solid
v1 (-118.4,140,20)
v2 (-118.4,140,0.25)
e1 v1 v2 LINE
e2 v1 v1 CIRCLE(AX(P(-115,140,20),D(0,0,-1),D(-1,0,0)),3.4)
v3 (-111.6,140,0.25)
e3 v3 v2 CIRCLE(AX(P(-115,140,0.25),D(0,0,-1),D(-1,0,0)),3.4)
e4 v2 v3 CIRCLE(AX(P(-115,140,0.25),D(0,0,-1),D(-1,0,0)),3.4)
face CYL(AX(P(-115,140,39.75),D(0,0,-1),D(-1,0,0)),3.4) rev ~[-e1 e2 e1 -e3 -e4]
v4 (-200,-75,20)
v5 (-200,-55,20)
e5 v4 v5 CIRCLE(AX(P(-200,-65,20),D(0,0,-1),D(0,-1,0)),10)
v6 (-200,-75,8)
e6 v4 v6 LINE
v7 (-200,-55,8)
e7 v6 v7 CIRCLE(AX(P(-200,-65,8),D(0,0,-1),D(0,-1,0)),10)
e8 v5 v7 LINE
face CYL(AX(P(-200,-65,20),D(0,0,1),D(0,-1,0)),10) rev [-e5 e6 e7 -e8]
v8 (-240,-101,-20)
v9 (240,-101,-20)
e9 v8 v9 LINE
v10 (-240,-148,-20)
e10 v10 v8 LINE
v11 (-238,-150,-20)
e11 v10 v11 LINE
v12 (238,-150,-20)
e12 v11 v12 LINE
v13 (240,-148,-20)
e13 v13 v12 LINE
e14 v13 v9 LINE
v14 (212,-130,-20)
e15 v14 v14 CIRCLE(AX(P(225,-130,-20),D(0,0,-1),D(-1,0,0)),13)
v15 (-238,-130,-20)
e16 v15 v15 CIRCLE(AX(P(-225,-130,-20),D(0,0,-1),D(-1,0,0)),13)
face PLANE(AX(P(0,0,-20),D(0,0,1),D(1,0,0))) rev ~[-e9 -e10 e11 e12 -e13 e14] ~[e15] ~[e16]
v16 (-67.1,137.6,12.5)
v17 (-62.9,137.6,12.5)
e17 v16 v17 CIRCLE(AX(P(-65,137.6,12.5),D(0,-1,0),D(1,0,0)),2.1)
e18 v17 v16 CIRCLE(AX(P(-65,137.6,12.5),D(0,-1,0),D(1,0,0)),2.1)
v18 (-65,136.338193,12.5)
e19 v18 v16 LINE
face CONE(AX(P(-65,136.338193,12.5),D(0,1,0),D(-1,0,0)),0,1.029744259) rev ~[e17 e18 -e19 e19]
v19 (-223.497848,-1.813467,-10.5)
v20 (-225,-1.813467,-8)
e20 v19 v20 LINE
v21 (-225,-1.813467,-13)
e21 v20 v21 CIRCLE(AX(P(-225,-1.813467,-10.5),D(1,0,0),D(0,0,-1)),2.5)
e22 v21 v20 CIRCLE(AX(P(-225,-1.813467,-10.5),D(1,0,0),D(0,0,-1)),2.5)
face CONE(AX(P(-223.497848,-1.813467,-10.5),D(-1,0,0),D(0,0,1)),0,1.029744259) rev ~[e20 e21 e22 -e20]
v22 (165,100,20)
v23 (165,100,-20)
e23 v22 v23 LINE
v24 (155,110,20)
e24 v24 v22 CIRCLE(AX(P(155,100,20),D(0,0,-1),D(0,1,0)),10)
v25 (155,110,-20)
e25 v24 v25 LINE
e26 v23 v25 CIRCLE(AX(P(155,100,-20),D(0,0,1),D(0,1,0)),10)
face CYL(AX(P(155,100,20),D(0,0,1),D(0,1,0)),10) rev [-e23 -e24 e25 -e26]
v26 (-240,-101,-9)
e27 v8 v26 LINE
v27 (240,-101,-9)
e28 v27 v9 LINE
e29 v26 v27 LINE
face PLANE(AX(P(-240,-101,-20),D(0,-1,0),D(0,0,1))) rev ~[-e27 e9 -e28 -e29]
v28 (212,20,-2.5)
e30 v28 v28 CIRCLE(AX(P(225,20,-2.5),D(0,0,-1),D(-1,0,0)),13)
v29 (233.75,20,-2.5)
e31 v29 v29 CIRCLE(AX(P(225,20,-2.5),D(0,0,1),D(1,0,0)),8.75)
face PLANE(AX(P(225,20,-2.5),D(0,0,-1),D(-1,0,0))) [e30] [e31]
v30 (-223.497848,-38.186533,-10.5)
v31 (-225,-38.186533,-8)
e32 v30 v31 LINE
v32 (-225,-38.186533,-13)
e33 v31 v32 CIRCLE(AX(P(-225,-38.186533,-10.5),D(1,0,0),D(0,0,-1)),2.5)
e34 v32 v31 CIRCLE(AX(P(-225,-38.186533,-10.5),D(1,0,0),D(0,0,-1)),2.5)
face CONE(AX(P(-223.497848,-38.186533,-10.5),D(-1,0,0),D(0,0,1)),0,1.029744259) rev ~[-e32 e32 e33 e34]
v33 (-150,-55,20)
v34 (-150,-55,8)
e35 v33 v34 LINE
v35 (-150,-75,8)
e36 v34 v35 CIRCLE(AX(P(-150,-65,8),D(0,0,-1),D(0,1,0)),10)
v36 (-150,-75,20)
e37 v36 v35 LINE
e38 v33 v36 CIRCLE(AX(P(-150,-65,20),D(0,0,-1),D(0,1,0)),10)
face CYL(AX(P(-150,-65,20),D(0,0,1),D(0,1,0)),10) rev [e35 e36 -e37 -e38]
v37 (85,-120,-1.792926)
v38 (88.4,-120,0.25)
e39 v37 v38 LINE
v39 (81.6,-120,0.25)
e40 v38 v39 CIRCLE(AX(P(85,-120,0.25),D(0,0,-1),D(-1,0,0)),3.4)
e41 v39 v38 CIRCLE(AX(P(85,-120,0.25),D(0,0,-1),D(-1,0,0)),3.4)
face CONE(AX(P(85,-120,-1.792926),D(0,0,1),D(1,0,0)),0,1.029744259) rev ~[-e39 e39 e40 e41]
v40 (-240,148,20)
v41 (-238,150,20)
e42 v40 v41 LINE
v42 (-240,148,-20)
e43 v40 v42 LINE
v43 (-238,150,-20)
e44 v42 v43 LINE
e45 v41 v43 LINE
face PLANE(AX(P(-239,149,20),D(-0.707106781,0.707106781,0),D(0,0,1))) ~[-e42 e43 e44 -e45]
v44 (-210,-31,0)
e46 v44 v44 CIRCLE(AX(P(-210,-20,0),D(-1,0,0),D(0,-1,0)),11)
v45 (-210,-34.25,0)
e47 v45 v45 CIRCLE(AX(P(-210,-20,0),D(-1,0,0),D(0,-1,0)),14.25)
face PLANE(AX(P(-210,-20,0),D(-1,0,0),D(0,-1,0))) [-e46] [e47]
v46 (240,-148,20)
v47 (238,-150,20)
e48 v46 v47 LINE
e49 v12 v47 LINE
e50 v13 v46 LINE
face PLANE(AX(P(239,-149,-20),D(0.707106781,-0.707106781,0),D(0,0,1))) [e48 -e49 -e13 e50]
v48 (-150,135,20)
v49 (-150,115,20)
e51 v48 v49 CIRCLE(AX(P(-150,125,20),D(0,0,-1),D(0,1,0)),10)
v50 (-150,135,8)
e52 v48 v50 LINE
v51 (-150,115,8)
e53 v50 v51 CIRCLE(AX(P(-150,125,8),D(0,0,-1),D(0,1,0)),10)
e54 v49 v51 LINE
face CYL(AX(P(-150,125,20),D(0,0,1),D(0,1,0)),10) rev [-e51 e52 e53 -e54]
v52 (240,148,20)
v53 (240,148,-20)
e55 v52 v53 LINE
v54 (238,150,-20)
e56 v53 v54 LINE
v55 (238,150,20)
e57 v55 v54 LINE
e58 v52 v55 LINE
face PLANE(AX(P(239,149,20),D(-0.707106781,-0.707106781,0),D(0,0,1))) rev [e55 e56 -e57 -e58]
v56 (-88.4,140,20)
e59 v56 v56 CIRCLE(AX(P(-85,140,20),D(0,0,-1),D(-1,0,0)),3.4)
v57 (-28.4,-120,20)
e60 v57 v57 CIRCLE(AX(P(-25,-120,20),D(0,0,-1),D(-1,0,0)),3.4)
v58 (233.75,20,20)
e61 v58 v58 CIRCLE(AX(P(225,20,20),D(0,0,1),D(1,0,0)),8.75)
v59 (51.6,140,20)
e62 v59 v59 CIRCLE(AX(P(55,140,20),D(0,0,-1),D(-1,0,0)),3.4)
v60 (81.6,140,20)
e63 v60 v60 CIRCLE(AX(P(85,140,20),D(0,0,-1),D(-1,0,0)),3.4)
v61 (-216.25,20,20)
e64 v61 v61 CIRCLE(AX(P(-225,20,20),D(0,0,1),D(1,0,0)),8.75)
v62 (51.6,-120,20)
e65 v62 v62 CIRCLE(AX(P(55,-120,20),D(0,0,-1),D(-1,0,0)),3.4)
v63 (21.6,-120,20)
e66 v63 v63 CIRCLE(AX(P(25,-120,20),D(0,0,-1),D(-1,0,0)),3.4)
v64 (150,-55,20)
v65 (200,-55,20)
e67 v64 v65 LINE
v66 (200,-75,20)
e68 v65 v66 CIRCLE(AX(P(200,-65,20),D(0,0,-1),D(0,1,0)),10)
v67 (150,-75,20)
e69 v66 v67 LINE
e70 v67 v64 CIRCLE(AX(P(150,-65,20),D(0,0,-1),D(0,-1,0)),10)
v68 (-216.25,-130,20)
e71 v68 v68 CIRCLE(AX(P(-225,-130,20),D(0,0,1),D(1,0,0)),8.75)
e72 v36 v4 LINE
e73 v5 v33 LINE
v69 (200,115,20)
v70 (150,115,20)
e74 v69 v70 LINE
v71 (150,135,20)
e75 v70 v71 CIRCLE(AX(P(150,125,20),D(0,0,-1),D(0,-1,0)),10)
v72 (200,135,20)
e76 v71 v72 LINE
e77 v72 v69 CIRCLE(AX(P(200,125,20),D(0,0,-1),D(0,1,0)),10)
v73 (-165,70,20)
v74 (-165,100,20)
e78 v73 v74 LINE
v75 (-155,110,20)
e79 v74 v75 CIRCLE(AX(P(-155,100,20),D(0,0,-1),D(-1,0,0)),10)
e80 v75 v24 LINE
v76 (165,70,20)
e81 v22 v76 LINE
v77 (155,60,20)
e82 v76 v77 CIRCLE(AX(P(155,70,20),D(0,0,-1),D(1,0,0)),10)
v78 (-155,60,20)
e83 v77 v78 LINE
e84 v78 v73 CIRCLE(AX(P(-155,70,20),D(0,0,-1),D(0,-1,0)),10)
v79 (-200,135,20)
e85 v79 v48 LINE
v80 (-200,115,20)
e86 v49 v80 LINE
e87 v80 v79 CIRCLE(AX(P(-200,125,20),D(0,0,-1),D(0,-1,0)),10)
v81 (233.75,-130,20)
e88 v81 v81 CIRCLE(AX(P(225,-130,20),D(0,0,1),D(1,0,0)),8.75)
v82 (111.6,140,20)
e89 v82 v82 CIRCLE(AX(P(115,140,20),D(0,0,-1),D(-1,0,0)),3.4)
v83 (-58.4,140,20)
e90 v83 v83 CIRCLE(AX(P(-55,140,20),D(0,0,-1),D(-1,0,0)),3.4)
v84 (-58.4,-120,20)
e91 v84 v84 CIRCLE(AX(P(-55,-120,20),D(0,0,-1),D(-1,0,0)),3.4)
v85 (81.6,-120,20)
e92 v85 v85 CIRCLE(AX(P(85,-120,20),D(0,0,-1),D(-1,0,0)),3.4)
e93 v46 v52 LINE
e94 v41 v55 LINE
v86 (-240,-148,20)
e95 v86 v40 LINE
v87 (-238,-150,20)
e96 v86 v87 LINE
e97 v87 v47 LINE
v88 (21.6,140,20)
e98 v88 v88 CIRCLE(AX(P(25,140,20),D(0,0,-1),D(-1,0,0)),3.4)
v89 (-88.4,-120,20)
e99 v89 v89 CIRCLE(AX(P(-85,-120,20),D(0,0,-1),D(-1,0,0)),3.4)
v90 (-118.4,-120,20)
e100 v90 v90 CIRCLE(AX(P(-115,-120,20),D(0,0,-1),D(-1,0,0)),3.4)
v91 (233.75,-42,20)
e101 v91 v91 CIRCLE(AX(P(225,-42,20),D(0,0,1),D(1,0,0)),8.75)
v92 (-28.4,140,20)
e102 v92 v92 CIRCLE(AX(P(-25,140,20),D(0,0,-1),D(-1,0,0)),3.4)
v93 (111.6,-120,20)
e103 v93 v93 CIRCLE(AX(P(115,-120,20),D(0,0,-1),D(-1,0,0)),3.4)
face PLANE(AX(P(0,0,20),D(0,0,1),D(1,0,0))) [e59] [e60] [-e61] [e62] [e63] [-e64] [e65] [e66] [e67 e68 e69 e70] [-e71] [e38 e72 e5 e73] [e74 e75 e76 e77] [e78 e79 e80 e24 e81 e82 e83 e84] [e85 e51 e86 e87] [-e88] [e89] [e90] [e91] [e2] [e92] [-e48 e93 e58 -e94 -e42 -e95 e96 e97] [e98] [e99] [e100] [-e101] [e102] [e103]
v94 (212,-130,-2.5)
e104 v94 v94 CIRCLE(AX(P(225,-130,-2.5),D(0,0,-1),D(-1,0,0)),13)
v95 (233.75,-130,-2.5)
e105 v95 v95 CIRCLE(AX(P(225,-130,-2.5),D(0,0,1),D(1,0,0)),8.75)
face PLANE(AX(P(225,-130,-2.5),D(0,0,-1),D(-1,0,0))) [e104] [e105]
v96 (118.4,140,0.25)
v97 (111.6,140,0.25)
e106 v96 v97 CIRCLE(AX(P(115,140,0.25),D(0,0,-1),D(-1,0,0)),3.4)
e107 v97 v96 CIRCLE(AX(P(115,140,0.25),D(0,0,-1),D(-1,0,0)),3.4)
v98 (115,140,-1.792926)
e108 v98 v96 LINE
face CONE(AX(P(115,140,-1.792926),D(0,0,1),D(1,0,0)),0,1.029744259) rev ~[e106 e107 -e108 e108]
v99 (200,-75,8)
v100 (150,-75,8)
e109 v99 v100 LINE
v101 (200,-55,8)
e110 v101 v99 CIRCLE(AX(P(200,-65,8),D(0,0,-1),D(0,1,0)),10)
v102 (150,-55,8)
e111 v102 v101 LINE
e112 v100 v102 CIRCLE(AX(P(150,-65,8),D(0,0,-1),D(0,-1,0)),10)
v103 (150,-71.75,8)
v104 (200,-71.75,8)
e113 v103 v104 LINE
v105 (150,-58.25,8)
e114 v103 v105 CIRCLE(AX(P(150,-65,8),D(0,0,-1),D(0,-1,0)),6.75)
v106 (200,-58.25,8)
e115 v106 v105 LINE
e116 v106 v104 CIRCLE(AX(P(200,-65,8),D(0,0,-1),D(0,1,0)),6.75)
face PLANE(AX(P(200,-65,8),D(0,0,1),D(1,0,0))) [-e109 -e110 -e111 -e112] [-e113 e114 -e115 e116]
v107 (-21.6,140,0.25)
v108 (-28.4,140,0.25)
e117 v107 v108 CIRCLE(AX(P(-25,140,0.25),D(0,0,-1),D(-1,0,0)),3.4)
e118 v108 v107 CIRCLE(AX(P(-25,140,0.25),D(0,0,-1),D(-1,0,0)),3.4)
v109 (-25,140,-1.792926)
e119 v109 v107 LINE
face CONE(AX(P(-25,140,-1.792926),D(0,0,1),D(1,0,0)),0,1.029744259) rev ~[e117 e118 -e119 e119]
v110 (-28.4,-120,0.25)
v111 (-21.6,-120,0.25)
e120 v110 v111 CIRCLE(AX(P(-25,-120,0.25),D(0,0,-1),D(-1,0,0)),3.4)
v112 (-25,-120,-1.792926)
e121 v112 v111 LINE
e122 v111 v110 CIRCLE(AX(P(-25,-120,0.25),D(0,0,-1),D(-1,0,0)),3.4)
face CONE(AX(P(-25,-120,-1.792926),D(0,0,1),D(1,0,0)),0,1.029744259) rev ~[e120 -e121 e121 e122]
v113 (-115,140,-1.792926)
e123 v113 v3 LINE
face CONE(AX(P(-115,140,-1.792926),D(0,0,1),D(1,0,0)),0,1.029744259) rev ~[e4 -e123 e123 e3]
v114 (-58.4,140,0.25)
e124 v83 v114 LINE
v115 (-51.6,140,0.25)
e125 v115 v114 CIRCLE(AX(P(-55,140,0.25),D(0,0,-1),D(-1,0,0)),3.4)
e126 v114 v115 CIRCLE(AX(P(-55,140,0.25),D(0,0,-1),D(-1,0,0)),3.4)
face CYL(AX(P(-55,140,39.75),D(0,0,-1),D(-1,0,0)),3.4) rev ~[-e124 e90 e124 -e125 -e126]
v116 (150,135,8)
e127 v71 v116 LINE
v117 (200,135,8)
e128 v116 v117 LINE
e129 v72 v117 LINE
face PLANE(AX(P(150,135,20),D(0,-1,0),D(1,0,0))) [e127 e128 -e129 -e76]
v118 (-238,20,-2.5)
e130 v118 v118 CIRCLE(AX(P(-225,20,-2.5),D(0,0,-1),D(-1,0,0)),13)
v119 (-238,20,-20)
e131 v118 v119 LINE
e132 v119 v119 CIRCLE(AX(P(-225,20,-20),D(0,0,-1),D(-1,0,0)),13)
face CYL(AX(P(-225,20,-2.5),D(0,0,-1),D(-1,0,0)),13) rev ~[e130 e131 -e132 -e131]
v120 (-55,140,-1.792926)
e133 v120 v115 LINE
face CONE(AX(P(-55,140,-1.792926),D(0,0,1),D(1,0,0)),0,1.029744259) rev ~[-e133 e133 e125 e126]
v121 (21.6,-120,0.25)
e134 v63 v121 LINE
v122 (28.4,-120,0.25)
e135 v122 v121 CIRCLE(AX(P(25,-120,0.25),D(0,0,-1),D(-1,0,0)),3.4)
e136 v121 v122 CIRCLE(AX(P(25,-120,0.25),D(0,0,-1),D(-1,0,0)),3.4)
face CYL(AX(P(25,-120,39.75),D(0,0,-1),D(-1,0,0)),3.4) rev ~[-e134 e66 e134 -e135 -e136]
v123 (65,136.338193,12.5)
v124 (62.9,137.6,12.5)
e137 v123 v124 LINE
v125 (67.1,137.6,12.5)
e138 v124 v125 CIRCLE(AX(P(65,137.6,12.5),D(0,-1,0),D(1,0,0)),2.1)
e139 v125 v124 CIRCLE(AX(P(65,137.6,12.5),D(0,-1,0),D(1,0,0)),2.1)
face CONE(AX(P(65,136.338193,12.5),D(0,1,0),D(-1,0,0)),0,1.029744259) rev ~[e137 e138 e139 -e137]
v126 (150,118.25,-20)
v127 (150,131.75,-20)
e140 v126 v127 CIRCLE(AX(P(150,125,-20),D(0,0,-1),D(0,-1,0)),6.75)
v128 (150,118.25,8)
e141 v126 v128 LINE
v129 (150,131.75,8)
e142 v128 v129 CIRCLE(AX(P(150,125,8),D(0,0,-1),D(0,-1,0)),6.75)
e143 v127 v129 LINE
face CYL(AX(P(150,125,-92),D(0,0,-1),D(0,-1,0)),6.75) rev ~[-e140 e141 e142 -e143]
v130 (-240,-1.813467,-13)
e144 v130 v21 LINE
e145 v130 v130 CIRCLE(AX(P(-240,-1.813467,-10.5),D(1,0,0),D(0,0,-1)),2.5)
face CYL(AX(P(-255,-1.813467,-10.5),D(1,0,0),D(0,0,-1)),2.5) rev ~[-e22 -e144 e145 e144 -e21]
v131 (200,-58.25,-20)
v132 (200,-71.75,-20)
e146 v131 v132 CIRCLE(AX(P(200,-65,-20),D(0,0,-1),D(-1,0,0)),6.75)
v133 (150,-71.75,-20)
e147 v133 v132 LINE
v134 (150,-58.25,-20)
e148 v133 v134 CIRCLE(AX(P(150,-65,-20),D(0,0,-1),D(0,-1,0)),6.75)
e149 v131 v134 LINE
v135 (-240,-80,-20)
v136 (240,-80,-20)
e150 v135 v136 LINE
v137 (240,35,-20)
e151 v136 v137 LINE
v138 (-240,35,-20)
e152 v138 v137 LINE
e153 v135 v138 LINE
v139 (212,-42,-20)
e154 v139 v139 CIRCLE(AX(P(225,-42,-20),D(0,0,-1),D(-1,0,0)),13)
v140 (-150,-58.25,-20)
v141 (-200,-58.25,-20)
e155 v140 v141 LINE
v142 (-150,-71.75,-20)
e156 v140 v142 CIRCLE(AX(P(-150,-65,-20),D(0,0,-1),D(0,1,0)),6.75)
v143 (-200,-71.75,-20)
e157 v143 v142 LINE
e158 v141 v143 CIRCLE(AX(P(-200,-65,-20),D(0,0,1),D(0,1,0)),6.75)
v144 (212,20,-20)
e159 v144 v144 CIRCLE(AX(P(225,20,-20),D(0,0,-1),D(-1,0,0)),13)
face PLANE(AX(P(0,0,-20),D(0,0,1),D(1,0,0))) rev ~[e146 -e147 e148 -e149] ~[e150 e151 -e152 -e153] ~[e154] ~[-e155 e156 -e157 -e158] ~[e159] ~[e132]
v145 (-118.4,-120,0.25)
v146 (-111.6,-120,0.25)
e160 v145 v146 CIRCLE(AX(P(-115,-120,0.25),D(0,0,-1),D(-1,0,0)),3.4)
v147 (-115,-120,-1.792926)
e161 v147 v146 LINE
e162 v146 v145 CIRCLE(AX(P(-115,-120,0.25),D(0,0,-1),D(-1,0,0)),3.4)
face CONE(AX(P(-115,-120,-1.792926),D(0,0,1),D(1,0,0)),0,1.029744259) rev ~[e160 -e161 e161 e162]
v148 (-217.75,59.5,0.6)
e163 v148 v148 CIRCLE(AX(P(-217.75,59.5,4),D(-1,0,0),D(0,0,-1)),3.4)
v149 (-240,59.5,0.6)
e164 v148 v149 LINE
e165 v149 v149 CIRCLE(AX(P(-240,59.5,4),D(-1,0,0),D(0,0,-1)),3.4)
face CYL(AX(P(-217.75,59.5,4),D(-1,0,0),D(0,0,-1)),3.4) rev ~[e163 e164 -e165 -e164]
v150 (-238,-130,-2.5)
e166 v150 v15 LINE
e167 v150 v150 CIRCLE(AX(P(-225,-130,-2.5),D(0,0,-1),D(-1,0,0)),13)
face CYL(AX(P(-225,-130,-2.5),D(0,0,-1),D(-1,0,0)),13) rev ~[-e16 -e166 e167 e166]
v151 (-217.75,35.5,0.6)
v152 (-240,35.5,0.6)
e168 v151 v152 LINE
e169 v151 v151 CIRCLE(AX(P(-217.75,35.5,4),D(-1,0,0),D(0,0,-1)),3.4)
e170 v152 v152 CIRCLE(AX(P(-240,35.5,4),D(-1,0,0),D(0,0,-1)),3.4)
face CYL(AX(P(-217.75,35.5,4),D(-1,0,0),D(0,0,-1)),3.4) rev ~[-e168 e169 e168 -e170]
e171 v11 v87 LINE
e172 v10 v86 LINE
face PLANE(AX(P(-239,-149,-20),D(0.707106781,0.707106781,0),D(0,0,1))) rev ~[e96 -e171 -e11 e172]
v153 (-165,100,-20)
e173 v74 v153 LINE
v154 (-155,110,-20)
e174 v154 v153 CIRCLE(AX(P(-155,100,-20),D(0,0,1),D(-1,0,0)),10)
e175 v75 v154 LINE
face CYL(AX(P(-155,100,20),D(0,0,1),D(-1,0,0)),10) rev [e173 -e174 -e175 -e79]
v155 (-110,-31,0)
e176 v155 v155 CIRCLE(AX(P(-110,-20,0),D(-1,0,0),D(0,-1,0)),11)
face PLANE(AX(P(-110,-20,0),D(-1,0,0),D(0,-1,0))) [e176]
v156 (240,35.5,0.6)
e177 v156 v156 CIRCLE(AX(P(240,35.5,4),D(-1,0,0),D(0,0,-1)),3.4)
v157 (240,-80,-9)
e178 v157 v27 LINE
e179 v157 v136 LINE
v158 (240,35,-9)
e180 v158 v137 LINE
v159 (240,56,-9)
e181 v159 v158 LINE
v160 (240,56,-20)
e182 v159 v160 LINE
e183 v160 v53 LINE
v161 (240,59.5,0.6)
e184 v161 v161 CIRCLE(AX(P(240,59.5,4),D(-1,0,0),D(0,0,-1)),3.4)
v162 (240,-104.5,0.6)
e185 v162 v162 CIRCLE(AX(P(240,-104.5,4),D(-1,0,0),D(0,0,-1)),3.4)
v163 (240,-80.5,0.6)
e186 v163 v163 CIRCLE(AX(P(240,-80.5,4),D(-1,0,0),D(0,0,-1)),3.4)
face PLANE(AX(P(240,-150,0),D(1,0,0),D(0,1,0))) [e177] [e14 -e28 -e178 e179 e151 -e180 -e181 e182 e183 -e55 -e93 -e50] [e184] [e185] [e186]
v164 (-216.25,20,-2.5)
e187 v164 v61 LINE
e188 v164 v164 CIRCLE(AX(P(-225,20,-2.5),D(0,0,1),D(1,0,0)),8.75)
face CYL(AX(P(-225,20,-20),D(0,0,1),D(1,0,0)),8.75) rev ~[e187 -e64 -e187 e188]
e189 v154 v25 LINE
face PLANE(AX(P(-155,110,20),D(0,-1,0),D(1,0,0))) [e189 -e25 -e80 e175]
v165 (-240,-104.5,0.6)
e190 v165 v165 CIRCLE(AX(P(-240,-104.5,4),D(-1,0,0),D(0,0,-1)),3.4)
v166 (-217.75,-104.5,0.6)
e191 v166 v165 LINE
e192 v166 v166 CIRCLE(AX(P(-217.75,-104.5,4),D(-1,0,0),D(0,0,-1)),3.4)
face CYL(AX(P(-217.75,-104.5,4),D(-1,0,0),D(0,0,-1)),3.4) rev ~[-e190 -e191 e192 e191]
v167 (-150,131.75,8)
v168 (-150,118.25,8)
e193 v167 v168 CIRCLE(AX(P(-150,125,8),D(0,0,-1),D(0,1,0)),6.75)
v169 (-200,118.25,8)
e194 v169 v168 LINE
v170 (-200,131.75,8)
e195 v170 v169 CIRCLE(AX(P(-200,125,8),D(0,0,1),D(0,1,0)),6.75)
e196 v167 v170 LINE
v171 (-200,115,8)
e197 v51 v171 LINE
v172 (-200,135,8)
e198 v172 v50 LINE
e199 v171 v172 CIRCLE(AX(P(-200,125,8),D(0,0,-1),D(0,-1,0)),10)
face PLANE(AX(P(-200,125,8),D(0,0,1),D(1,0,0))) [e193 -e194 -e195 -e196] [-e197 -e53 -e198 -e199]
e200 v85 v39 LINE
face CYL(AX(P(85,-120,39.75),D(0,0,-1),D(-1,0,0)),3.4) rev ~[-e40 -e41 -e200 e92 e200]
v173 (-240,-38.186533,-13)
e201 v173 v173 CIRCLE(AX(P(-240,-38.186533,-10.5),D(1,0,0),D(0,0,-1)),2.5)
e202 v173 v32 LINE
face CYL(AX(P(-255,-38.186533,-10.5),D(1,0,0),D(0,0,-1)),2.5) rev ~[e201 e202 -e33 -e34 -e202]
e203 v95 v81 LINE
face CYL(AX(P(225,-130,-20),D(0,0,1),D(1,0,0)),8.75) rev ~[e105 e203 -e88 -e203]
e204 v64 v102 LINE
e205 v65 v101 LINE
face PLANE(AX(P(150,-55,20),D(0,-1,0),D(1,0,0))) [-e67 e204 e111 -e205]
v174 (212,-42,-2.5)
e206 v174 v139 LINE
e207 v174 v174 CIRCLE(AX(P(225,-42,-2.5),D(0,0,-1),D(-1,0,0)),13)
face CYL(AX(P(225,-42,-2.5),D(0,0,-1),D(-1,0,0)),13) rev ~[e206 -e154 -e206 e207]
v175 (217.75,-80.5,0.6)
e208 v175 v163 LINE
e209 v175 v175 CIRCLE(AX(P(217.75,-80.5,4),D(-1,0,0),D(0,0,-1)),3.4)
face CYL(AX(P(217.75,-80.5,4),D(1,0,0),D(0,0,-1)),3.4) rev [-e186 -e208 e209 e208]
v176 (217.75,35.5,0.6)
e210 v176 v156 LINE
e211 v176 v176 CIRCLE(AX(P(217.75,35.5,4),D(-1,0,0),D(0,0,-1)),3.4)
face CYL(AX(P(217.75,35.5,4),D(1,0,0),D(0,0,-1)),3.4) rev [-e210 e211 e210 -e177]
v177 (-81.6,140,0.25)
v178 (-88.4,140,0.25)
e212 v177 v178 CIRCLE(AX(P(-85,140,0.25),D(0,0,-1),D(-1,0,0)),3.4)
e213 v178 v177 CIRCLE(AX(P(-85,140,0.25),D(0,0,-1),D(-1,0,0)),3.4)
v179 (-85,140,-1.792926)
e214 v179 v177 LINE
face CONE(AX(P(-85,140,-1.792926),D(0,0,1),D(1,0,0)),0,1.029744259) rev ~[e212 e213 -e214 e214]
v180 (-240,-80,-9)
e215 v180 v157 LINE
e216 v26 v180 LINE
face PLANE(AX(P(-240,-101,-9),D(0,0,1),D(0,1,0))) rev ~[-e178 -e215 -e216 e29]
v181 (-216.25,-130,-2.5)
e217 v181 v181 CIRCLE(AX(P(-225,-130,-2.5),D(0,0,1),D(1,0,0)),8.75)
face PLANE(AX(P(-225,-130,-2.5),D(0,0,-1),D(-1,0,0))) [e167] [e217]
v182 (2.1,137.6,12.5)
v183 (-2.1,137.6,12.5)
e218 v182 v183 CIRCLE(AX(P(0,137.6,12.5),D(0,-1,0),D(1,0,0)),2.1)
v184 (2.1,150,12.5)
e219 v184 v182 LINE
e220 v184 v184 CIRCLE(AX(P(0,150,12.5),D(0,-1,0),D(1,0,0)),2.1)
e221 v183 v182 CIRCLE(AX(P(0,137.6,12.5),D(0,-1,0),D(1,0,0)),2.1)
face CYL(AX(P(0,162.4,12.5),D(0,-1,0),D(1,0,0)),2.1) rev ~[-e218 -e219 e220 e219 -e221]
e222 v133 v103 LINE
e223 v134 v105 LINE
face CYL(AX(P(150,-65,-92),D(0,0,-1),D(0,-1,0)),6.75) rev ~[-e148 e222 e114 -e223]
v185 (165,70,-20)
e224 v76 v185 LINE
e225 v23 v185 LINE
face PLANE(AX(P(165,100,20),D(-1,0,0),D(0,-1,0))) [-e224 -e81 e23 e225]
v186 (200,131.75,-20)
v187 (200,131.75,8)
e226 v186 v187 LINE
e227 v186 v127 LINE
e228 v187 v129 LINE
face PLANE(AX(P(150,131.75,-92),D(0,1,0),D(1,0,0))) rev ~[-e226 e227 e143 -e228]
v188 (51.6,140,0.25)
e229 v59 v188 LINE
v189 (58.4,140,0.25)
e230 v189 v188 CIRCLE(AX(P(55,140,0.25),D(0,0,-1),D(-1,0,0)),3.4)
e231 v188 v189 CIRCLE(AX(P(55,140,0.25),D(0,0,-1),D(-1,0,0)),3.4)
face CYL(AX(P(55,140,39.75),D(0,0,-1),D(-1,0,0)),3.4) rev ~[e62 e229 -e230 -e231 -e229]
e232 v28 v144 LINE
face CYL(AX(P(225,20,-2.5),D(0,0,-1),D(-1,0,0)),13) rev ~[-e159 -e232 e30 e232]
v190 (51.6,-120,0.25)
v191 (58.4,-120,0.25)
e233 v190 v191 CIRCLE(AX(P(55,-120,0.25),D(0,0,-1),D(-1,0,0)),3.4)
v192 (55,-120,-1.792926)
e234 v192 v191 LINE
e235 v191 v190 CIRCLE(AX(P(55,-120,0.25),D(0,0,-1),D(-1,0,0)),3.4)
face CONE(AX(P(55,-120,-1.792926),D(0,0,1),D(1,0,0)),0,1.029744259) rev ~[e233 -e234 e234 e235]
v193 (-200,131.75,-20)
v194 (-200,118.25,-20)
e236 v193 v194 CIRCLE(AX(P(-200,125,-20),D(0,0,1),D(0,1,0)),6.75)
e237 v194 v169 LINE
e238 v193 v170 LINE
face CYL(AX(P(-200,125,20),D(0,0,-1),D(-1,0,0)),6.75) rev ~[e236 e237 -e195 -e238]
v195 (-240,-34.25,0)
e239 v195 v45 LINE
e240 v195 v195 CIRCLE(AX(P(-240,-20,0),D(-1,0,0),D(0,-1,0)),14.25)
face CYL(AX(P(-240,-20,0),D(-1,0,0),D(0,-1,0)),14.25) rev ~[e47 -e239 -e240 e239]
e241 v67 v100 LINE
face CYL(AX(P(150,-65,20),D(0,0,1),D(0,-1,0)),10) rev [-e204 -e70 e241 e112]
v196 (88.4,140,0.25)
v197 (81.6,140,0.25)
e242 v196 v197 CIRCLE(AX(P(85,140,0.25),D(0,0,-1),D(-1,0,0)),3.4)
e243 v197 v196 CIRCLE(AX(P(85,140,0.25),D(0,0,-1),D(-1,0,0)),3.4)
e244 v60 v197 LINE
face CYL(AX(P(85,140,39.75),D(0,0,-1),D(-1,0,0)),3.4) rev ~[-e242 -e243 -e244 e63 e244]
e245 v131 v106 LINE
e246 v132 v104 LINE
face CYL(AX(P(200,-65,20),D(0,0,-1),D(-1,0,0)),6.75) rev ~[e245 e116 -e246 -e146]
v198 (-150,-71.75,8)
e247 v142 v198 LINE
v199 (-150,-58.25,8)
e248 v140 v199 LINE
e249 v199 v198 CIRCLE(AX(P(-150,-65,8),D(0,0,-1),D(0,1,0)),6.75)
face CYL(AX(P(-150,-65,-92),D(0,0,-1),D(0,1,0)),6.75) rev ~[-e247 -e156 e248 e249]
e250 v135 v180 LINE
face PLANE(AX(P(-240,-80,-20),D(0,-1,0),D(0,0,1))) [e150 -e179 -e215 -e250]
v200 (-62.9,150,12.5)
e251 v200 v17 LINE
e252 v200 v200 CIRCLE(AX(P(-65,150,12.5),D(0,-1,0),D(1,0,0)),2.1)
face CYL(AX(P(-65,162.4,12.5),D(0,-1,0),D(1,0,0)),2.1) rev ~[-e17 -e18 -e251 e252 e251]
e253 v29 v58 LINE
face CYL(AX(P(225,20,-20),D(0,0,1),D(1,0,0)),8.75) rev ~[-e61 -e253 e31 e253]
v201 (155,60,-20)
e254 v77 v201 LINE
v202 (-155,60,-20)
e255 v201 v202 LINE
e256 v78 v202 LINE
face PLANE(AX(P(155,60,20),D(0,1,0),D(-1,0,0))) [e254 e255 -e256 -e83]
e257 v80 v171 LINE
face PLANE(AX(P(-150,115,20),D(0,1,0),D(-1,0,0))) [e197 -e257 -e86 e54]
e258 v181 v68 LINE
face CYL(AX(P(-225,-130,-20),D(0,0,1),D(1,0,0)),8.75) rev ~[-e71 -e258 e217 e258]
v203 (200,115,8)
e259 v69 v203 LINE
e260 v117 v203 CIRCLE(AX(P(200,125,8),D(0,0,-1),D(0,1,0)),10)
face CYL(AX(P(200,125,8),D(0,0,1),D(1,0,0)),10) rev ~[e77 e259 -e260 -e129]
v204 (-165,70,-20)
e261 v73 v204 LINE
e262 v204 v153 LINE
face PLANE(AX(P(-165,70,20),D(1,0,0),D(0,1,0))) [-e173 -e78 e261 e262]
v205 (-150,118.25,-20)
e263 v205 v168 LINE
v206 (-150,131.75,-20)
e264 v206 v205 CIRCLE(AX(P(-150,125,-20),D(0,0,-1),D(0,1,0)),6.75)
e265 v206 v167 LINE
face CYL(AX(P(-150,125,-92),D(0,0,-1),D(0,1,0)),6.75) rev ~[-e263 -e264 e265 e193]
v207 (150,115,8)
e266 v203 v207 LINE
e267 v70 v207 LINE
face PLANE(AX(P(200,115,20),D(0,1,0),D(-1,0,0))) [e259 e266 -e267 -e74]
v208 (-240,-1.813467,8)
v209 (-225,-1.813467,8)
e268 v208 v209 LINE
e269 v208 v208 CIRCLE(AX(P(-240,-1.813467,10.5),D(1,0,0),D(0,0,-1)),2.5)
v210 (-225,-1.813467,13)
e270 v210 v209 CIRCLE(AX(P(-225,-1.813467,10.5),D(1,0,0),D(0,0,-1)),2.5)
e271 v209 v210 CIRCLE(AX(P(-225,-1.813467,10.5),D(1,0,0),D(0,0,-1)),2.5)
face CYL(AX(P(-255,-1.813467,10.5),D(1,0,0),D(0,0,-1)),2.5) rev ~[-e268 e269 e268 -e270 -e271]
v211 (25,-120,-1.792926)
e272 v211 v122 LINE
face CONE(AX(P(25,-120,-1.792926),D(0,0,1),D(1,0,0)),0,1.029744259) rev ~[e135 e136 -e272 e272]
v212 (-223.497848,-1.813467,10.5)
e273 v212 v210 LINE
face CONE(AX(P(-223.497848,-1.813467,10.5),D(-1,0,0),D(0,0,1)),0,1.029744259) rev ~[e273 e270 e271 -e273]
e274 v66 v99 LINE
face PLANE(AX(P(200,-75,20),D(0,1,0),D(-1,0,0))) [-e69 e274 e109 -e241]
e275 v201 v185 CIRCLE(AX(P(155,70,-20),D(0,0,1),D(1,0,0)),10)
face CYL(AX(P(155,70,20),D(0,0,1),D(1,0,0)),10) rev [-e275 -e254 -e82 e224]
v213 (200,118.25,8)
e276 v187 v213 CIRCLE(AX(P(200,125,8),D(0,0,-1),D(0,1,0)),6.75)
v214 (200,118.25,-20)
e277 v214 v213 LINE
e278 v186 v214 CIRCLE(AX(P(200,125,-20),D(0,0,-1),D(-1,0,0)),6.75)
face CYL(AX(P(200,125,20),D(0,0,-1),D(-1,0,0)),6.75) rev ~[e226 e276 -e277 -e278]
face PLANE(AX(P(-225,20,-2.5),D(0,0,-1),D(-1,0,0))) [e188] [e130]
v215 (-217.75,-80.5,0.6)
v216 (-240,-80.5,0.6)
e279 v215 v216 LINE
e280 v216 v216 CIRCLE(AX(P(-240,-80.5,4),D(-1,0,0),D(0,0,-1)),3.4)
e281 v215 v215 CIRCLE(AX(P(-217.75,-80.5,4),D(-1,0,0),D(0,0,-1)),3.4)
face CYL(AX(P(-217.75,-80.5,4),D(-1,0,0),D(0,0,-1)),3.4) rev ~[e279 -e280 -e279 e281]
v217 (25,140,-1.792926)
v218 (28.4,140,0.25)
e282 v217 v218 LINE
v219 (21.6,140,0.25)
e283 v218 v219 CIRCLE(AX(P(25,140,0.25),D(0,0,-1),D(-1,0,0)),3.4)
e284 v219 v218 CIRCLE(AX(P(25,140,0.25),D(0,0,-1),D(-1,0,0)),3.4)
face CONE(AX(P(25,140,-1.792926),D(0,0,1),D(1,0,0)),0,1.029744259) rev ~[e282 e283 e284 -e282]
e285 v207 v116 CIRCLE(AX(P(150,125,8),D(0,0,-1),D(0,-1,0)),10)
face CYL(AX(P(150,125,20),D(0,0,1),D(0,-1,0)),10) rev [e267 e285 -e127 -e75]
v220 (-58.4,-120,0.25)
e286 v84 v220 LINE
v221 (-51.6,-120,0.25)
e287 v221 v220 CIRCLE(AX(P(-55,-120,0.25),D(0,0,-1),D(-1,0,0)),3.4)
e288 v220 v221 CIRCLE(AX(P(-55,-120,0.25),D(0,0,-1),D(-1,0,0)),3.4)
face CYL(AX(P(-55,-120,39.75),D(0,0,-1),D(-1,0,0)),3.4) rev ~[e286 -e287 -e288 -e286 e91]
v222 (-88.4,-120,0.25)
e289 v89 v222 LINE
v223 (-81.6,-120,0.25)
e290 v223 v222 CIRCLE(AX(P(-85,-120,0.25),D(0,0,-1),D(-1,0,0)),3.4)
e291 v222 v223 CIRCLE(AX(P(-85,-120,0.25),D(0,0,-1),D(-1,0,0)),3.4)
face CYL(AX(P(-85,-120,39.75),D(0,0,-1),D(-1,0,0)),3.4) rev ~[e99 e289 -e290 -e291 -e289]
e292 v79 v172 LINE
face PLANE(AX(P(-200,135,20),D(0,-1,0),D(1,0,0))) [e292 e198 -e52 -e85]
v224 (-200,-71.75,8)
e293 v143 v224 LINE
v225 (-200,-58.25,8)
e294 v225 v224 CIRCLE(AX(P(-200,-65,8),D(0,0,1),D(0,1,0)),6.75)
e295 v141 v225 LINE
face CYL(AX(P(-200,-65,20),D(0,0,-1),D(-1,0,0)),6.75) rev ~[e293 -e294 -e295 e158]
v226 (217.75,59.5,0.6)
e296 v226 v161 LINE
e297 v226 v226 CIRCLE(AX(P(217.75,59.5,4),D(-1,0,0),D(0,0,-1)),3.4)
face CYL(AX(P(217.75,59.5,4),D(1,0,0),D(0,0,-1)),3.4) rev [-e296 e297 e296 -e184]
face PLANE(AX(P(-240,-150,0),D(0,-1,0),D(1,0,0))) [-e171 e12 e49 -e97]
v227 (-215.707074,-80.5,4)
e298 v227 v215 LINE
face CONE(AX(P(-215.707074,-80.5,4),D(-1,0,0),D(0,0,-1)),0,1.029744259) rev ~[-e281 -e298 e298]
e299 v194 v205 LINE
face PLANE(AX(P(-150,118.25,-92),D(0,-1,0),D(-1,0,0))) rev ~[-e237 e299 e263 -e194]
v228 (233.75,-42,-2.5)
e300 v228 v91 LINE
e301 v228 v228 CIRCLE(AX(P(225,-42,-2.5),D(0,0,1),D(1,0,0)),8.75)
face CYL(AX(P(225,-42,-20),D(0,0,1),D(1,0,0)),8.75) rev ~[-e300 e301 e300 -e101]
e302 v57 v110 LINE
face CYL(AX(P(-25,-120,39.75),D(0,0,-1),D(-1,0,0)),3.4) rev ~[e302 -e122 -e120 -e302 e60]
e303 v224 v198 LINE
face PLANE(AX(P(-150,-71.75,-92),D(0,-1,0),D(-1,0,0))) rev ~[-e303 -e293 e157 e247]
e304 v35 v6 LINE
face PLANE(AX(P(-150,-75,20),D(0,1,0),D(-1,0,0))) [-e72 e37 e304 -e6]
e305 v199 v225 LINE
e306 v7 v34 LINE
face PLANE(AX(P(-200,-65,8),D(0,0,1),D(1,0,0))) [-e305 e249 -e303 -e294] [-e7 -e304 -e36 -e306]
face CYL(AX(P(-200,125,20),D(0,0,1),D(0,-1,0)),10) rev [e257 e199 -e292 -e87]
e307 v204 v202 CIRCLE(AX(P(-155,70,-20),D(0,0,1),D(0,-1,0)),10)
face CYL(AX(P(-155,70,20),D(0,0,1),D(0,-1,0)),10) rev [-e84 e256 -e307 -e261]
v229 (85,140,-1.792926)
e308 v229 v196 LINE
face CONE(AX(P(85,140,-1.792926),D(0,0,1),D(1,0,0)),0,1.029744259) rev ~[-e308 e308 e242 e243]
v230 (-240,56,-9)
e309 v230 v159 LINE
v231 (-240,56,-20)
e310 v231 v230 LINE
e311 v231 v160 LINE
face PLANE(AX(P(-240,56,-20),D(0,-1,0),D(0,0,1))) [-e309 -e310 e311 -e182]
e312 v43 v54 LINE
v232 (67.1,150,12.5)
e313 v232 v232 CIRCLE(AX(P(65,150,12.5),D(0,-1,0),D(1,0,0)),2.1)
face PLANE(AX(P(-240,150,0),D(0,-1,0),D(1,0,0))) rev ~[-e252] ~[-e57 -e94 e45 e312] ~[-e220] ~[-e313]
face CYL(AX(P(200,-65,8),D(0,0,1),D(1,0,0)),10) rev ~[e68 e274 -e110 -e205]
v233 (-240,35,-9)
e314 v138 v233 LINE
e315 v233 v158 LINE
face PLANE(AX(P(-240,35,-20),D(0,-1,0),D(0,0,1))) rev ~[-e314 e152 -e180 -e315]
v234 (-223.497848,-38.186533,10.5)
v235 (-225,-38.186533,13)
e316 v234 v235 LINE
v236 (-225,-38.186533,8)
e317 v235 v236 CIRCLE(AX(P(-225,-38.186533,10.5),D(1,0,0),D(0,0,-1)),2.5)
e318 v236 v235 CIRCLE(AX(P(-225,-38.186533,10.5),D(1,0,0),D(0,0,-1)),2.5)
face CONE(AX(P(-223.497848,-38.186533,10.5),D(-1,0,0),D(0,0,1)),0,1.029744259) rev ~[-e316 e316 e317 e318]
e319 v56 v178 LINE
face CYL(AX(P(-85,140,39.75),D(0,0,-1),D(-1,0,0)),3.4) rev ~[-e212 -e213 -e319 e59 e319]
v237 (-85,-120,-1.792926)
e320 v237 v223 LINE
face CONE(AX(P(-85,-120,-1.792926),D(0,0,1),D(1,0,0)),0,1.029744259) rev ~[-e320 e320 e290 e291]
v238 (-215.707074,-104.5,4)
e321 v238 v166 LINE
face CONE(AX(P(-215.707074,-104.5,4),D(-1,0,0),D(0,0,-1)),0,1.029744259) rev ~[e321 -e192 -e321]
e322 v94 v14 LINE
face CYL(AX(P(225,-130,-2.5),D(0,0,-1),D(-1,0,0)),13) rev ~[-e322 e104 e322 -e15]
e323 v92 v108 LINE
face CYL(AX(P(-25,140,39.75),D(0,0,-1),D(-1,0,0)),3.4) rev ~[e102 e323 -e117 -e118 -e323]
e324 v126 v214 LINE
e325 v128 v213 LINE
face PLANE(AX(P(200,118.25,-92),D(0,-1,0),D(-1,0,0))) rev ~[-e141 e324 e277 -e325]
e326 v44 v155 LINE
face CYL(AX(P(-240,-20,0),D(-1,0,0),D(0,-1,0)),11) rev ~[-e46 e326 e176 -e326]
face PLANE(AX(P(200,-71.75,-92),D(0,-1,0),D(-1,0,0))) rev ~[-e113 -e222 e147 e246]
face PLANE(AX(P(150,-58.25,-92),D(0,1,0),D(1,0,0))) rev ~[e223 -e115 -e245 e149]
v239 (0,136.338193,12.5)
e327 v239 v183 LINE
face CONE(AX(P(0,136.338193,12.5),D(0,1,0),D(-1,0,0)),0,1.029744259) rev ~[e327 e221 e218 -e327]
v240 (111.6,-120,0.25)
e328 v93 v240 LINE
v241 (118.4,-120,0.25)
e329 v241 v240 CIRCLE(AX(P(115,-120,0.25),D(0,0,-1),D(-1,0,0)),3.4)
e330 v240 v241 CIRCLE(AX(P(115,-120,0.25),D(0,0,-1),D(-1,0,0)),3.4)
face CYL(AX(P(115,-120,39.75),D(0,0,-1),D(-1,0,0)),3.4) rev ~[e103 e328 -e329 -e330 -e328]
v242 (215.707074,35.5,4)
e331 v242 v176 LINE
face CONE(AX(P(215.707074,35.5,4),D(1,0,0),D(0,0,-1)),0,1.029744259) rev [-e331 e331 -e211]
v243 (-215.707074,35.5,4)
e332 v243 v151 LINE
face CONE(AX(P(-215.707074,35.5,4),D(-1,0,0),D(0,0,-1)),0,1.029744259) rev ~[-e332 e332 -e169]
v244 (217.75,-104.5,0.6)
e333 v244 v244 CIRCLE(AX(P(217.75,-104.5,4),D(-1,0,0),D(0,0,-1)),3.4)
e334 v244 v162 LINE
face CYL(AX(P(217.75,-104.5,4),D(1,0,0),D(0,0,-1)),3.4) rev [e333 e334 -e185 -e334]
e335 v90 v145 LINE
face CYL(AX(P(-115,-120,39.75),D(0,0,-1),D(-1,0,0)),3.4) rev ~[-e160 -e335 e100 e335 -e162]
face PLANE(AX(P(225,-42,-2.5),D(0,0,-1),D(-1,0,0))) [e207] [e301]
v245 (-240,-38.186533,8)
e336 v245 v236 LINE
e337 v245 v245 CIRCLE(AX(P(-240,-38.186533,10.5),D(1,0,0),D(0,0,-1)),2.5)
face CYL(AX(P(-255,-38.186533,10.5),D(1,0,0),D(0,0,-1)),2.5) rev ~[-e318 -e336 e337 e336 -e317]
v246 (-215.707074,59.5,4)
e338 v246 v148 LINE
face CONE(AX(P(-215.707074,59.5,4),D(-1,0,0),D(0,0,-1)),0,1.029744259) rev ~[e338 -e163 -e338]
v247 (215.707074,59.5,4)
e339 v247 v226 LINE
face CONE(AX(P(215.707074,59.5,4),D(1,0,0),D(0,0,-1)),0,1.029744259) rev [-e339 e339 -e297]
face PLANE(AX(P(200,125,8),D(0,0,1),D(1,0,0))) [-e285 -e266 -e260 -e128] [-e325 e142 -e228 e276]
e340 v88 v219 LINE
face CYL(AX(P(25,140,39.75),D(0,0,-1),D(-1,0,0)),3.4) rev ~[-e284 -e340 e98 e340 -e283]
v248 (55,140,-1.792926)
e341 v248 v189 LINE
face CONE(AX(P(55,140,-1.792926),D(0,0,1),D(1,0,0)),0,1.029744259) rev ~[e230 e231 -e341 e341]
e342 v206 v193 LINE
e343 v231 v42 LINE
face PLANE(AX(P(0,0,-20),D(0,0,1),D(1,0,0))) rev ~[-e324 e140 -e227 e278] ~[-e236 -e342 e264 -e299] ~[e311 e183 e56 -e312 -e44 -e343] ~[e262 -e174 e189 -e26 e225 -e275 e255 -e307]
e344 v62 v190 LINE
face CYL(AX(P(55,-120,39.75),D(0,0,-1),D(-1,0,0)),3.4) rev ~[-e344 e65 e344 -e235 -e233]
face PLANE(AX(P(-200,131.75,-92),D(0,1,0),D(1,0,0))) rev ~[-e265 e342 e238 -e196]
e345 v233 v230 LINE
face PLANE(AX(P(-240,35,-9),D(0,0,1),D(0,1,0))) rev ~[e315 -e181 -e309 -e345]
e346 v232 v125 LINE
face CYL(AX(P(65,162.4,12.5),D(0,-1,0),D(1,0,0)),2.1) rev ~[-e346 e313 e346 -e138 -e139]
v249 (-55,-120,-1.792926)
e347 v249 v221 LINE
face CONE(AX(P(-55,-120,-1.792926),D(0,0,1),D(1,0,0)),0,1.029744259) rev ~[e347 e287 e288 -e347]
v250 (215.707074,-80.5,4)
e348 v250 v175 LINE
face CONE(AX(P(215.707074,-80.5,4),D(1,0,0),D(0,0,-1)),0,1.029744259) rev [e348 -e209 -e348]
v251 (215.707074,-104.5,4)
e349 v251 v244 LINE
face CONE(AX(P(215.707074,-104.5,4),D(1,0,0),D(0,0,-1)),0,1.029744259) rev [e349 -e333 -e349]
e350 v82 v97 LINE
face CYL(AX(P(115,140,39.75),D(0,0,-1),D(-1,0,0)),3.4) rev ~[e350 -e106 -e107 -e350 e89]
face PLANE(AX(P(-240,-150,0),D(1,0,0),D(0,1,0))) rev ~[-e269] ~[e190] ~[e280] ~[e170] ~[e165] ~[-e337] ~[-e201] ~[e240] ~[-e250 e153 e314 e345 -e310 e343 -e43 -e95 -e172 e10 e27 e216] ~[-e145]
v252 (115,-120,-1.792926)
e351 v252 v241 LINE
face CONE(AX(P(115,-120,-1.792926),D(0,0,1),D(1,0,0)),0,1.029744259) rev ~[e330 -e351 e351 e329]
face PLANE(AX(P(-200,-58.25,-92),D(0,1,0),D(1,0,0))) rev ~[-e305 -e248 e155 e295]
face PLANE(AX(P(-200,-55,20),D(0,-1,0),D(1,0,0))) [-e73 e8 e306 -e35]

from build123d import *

# Parameters (mm, degrees)
SKETCH1_W                                            = 480
SKETCH1_H                                            = 300
BOSS_EXTRUDE1_DEPTH                                  = 20
CUT_EXTRUDE1_DEPTH                                   = 286.832118559
HOLE_SIZE_PER_SOCKET_HEAD_CAP_SCREW_TYPE_D           = 17.5
HOLE_SIZE_PER_SOCKET_HEAD_CAP_SCREW_TYPE_CBORE_D     = 26
HOLE_SIZE_PER_SOCKET_HEAD_CAP_SCREW_TYPE_CBORE_DEPTH = 17.5
CBORE_FOR_M12_HEX_SOCKET_HEAD_CAP_SCREW1_D           = 13.5
CBORE_FOR_M12_HEX_SOCKET_HEAD_CAP_SCREW1_CBORE_D     = 20
CBORE_FOR_M12_HEX_SOCKET_HEAD_CAP_SCREW1_CBORE_DEPTH = 12
SKETCH7_W                                            = 11
SKETCH7_H                                            = 21
CUT_EXTRUDE2_DEPTH                                   = 504.289181286
M5_TAPPED_HOLE1_D                                    = 4.2
M5_TAPPED_HOLE1_DEPTH                                = 12.4
M5_TAPPED_HOLE1_TIP                                  = 1.2618073
CUT_EXTRUDE5_START                                   = -100
CUT_EXTRUDE5_DEPTH                                   = 100
CUT_EXTRUDE6_DEPTH                                   = 12
CHAMFER1_SIZE                                        = 2
M8_TAPPED_HOLE1_D                                    = 6.8
M8_TAPPED_HOLE1_DEPTH                                = 19.75
M8_TAPPED_HOLE1_TIP                                  = 2.042926105
SKETCH29_R                                           = 11
CUT_EXTRUDE7_DEPTH                                   = 130
SKETCH30_R                                           = 14.25
CUT_EXTRUDE8_DEPTH                                   = 30
M6_TAPPED_HOLE2_D                                    = 5
M6_TAPPED_HOLE2_DEPTH                                = 15
M6_TAPPED_HOLE2_TIP                                  = 1.502151548
M8_TAPPED_HOLE2_AT_2_COUNT                           = 2
M8_TAPPED_HOLE2_AT_2_PITCH                           = 24
M8_TAPPED_HOLE2_AT_3_COUNT                           = 2
M8_TAPPED_HOLE2_AT_3_PITCH                           = 116
M8_TAPPED_HOLE2_AT_4_COUNT                           = 2
M8_TAPPED_HOLE2_AT_4_PITCH                           = 140


with BuildPart() as part:
    # Sketch1 → Boss-Extrude1 (new, symmetric)
    with BuildSketch(Plane.XY):
        Rectangle(SKETCH1_W, SKETCH1_H)
    extrude(amount=BOSS_EXTRUDE1_DEPTH, both=True)

    # Sketch2 → Cut-Extrude1 (cut, through all)
    with BuildSketch(Plane.XY.offset(20)):
        with BuildLine():
            Line((-155, 110), (155, 110))
            ThreePointArc((155, 110), (162.071067812, 107.071067812), (165, 100))
            Line((165, 100), (165, 70))
            ThreePointArc((165, 70), (162.071067812, 62.928932188), (155, 60))
            Line((155, 60), (-155, 60))
            ThreePointArc((-155, 60), (-162.071067812, 62.928932188), (-165, 70))
            Line((-165, 70), (-165, 100))
            ThreePointArc((-165, 100), (-162.071067812, 107.071067812), (-155, 110))
        make_face()
    extrude(amount=-CUT_EXTRUDE1_DEPTH, mode=Mode.SUBTRACT)

    # Hole size per socket head cap screw type2 (through all)
    with Locations(Plane(origin=(0, 0, -20), x_dir=(-1, 0, 0), z_dir=(0, 0, -1))):
        with Locations((-225, 20), (225, 20), (225, -130), (-225, -130), (-225, -42)):
            CounterBoreHole(HOLE_SIZE_PER_SOCKET_HEAD_CAP_SCREW_TYPE_D / 2, HOLE_SIZE_PER_SOCKET_HEAD_CAP_SCREW_TYPE_CBORE_D / 2, HOLE_SIZE_PER_SOCKET_HEAD_CAP_SCREW_TYPE_CBORE_DEPTH)

    # CBORE for M12 Hex Socket Head Cap Screw1 (through all)
    with Locations(Plane.XY.offset(20)):
        with Locations((-200, 125), (200, 125), (-200, -65), (200, -65)):
            CounterBoreHole(CBORE_FOR_M12_HEX_SOCKET_HEAD_CAP_SCREW1_D / 2, CBORE_FOR_M12_HEX_SOCKET_HEAD_CAP_SCREW1_CBORE_D / 2, CBORE_FOR_M12_HEX_SOCKET_HEAD_CAP_SCREW1_CBORE_DEPTH)

    # Sketch7 → Cut-Extrude2 (cut, through all)
    with BuildSketch(Plane.ZY.offset(240)):
        with Locations((-14.5, -90.5)):
            Rectangle(SKETCH7_W, SKETCH7_H)
        with Locations((-14.5, 45.5)):
            Rectangle(SKETCH7_W, SKETCH7_H)
    extrude(amount=-CUT_EXTRUDE2_DEPTH, mode=Mode.SUBTRACT)

    # M5 Tapped Hole1
    with Locations(Plane(origin=(0, 150, 0), x_dir=(-1, 0, 0), z_dir=(0, 1, 0))):
        with Locations((0, 12.5), (-65, 12.5), (65, 12.5)):
            Hole(M5_TAPPED_HOLE1_D / 2, depth=M5_TAPPED_HOLE1_DEPTH)
            with Locations((0, 0, -(M5_TAPPED_HOLE1_DEPTH + M5_TAPPED_HOLE1_TIP / 2))):  # 118° drill point
                Cone(0, M5_TAPPED_HOLE1_D / 2, M5_TAPPED_HOLE1_TIP, mode=Mode.SUBTRACT)

    # Sketch14 → Cut-Extrude5 (cut)
    with BuildSketch(Plane.XY.offset(8).offset(CUT_EXTRUDE5_START)):
        with BuildLine():
            Line((-200, 131.75), (-150, 131.75))
            ThreePointArc((-150, 131.75), (-143.25, 125), (-150, 118.25))
            Line((-150, 118.25), (-200, 118.25))
            ThreePointArc((-200, 118.25), (-206.75, 125), (-200, 131.75))
        make_face()
        with BuildLine():
            Line((-200, -58.25), (-150, -58.25))
            ThreePointArc((-150, -58.25), (-143.25, -65), (-150, -71.75))
            Line((-150, -71.75), (-200, -71.75))
            ThreePointArc((-200, -71.75), (-206.75, -65), (-200, -58.25))
        make_face()
        with BuildLine():
            Line((200, -71.75), (150, -71.75))
            ThreePointArc((150, -71.75), (143.25, -65), (150, -58.25))
            Line((150, -58.25), (200, -58.25))
            ThreePointArc((200, -58.25), (206.75, -65), (200, -71.75))
        make_face()
        with BuildLine():
            Line((200, 118.25), (150, 118.25))
            ThreePointArc((150, 118.25), (143.25, 125), (150, 131.75))
            Line((150, 131.75), (200, 131.75))
            ThreePointArc((200, 131.75), (206.75, 125), (200, 118.25))
        make_face()
    extrude(amount=CUT_EXTRUDE5_DEPTH, mode=Mode.SUBTRACT)

    # Sketch15 → Cut-Extrude6 (cut)
    with BuildSketch(Plane.XY.offset(20)):
        with BuildLine():
            Line((-200, 135), (-150, 135))
            ThreePointArc((-150, 135), (-140, 125), (-150, 115))
            Line((-150, 115), (-200, 115))
            ThreePointArc((-200, 115), (-210, 125), (-200, 135))
        make_face()
        with BuildLine():
            Line((-200, -55), (-150, -55))
            ThreePointArc((-150, -55), (-140, -65), (-150, -75))
            Line((-150, -75), (-200, -75))
            ThreePointArc((-200, -75), (-210, -65), (-200, -55))
        make_face()
        with BuildLine():
            Line((200, -75), (150, -75))
            ThreePointArc((150, -75), (140, -65), (150, -55))
            Line((150, -55), (200, -55))
            ThreePointArc((200, -55), (210, -65), (200, -75))
        make_face()
        with BuildLine():
            Line((200, 115), (150, 115))
            ThreePointArc((150, 115), (140, 125), (150, 135))
            Line((150, 135), (200, 135))
            ThreePointArc((200, 135), (210, 125), (200, 115))
        make_face()
    extrude(amount=-CUT_EXTRUDE6_DEPTH, mode=Mode.SUBTRACT)

    # Chamfer1
    chamfer1_edges = [part.edges().sort_by_distance(p)[0] for p in [
        (240, -150, 0),
        (-240, -150, 0),
        (-240, 150, 0),
        (240, 150, 0),
    ]]
    chamfer(chamfer1_edges, length=CHAMFER1_SIZE)

    # M8 Tapped Hole1
    with Locations(Plane.XY.offset(20)):
        with Locations((55, 140), (-55, -120), (55, -120), (-55, 140), (-25, 140), (25, 140), (-85, 140), (85, 140), (-25, -120), (-85, -120), (85, -120), (25, -120), (-115, -120), (115, -120), (-115, 140), (115, 140)):
            Hole(M8_TAPPED_HOLE1_D / 2, depth=M8_TAPPED_HOLE1_DEPTH)
            with Locations((0, 0, -(M8_TAPPED_HOLE1_DEPTH + M8_TAPPED_HOLE1_TIP / 2))):  # 118° drill point
                Cone(0, M8_TAPPED_HOLE1_D / 2, M8_TAPPED_HOLE1_TIP, mode=Mode.SUBTRACT)

    # Sketch29 → Cut-Extrude7 (cut)
    with BuildSketch(Plane.ZY.offset(240)):
        with Locations(Location((0, -20, 0), (0, 0, 270))):
            Circle(SKETCH29_R)
    extrude(amount=-CUT_EXTRUDE7_DEPTH, mode=Mode.SUBTRACT)

    # Sketch30 → Cut-Extrude8 (cut)
    with BuildSketch(Plane.ZY.offset(240)):
        with Locations(Location((0, -20, 0), (0, 0, 270))):
            Circle(SKETCH30_R)
    extrude(amount=-CUT_EXTRUDE8_DEPTH, mode=Mode.SUBTRACT)

    # M6 Tapped Hole2
    with Locations(Plane.ZY.offset(240)):
        with Locations((-10.5, -1.813466521), (10.5, -1.813466521), (10.5, -38.186533479), (-10.5, -38.186533479)):
            Hole(M6_TAPPED_HOLE2_D / 2, depth=M6_TAPPED_HOLE2_DEPTH)
            with Locations((0, 0, -(M6_TAPPED_HOLE2_DEPTH + M6_TAPPED_HOLE2_TIP / 2))):  # 118° drill point
                Cone(0, M6_TAPPED_HOLE2_D / 2, M6_TAPPED_HOLE2_TIP, mode=Mode.SUBTRACT)

    # Sketch34 → M8 Tapped Hole2 (revolve, cut)
    with BuildSketch(Plane(origin=(240, -80.5, 4), x_dir=(0, 0, -1), z_dir=(0, 1, 0))):
        Polygon((0, 0), (0, 24.292926105), (3.4, 22.25), (3.4, 0), align=None)
    m8_tapped_hole2 = revolve(axis=Axis((246.35, -80.5, 4), (-1, 0, 0)), mode=Mode.SUBTRACT)

    # M8 Tapped Hole2 at 2: M8 Tapped Hole2 ×2
    with Locations(*[(0, -i * M8_TAPPED_HOLE2_AT_2_PITCH, 0) for i in range(1, M8_TAPPED_HOLE2_AT_2_COUNT)]):
        add(m8_tapped_hole2, mode=Mode.SUBTRACT)

    # M8 Tapped Hole2 at 3: M8 Tapped Hole2 ×2
    with Locations(*[(0, i * M8_TAPPED_HOLE2_AT_3_PITCH, 0) for i in range(1, M8_TAPPED_HOLE2_AT_3_COUNT)]):
        add(m8_tapped_hole2, mode=Mode.SUBTRACT)

    # M8 Tapped Hole2 at 4: M8 Tapped Hole2 ×2
    with Locations(*[(0, i * M8_TAPPED_HOLE2_AT_4_PITCH, 0) for i in range(1, M8_TAPPED_HOLE2_AT_4_COUNT)]):
        add(m8_tapped_hole2, mode=Mode.SUBTRACT)

    # Mirror1: M8 Tapped Hole2 across plane
    add(m8_tapped_hole2.mirror(Plane(origin=(0, 0, 0), x_dir=(0, 0, 1), z_dir=(1, 0, 0))), mode=Mode.SUBTRACT)

    # Mirror1 copy 1 sketch → Mirror1 copy 1 (revolve, cut)
    with BuildSketch(Plane(origin=(-240, -104.5, 4), x_dir=(0, 0, -1), z_dir=(0, 1, 0))):
        Polygon((0, 0), (0, -24.292926105), (3.4, -22.25), (3.4, 0), align=None)
    revolve(axis=Axis((-246.35, -104.5, 4), (-1, 0, 0)), mode=Mode.SUBTRACT)

    # Mirror1 copy 2 sketch → Mirror1 copy 2 (revolve, cut)
    with BuildSketch(Plane(origin=(-240, 35.5, 4), x_dir=(0, 0, -1), z_dir=(0, 1, 0))):
        Polygon((0, 0), (0, -24.292926105), (3.4, -22.25), (3.4, 0), align=None)
    revolve(axis=Axis((-246.35, 35.5, 4), (-1, 0, 0)), mode=Mode.SUBTRACT)

    # Mirror1 copy 3 sketch → Mirror1 copy 3 (revolve, cut)
    with BuildSketch(Plane(origin=(-240, 59.5, 4), x_dir=(0, 0, -1), z_dir=(0, 1, 0))):
        Polygon((0, 0), (0, -24.292926105), (3.4, -22.25), (3.4, 0), align=None)
    revolve(axis=Axis((-246.35, 59.5, 4), (-1, 0, 0)), mode=Mode.SUBTRACT)


solid = part.part
